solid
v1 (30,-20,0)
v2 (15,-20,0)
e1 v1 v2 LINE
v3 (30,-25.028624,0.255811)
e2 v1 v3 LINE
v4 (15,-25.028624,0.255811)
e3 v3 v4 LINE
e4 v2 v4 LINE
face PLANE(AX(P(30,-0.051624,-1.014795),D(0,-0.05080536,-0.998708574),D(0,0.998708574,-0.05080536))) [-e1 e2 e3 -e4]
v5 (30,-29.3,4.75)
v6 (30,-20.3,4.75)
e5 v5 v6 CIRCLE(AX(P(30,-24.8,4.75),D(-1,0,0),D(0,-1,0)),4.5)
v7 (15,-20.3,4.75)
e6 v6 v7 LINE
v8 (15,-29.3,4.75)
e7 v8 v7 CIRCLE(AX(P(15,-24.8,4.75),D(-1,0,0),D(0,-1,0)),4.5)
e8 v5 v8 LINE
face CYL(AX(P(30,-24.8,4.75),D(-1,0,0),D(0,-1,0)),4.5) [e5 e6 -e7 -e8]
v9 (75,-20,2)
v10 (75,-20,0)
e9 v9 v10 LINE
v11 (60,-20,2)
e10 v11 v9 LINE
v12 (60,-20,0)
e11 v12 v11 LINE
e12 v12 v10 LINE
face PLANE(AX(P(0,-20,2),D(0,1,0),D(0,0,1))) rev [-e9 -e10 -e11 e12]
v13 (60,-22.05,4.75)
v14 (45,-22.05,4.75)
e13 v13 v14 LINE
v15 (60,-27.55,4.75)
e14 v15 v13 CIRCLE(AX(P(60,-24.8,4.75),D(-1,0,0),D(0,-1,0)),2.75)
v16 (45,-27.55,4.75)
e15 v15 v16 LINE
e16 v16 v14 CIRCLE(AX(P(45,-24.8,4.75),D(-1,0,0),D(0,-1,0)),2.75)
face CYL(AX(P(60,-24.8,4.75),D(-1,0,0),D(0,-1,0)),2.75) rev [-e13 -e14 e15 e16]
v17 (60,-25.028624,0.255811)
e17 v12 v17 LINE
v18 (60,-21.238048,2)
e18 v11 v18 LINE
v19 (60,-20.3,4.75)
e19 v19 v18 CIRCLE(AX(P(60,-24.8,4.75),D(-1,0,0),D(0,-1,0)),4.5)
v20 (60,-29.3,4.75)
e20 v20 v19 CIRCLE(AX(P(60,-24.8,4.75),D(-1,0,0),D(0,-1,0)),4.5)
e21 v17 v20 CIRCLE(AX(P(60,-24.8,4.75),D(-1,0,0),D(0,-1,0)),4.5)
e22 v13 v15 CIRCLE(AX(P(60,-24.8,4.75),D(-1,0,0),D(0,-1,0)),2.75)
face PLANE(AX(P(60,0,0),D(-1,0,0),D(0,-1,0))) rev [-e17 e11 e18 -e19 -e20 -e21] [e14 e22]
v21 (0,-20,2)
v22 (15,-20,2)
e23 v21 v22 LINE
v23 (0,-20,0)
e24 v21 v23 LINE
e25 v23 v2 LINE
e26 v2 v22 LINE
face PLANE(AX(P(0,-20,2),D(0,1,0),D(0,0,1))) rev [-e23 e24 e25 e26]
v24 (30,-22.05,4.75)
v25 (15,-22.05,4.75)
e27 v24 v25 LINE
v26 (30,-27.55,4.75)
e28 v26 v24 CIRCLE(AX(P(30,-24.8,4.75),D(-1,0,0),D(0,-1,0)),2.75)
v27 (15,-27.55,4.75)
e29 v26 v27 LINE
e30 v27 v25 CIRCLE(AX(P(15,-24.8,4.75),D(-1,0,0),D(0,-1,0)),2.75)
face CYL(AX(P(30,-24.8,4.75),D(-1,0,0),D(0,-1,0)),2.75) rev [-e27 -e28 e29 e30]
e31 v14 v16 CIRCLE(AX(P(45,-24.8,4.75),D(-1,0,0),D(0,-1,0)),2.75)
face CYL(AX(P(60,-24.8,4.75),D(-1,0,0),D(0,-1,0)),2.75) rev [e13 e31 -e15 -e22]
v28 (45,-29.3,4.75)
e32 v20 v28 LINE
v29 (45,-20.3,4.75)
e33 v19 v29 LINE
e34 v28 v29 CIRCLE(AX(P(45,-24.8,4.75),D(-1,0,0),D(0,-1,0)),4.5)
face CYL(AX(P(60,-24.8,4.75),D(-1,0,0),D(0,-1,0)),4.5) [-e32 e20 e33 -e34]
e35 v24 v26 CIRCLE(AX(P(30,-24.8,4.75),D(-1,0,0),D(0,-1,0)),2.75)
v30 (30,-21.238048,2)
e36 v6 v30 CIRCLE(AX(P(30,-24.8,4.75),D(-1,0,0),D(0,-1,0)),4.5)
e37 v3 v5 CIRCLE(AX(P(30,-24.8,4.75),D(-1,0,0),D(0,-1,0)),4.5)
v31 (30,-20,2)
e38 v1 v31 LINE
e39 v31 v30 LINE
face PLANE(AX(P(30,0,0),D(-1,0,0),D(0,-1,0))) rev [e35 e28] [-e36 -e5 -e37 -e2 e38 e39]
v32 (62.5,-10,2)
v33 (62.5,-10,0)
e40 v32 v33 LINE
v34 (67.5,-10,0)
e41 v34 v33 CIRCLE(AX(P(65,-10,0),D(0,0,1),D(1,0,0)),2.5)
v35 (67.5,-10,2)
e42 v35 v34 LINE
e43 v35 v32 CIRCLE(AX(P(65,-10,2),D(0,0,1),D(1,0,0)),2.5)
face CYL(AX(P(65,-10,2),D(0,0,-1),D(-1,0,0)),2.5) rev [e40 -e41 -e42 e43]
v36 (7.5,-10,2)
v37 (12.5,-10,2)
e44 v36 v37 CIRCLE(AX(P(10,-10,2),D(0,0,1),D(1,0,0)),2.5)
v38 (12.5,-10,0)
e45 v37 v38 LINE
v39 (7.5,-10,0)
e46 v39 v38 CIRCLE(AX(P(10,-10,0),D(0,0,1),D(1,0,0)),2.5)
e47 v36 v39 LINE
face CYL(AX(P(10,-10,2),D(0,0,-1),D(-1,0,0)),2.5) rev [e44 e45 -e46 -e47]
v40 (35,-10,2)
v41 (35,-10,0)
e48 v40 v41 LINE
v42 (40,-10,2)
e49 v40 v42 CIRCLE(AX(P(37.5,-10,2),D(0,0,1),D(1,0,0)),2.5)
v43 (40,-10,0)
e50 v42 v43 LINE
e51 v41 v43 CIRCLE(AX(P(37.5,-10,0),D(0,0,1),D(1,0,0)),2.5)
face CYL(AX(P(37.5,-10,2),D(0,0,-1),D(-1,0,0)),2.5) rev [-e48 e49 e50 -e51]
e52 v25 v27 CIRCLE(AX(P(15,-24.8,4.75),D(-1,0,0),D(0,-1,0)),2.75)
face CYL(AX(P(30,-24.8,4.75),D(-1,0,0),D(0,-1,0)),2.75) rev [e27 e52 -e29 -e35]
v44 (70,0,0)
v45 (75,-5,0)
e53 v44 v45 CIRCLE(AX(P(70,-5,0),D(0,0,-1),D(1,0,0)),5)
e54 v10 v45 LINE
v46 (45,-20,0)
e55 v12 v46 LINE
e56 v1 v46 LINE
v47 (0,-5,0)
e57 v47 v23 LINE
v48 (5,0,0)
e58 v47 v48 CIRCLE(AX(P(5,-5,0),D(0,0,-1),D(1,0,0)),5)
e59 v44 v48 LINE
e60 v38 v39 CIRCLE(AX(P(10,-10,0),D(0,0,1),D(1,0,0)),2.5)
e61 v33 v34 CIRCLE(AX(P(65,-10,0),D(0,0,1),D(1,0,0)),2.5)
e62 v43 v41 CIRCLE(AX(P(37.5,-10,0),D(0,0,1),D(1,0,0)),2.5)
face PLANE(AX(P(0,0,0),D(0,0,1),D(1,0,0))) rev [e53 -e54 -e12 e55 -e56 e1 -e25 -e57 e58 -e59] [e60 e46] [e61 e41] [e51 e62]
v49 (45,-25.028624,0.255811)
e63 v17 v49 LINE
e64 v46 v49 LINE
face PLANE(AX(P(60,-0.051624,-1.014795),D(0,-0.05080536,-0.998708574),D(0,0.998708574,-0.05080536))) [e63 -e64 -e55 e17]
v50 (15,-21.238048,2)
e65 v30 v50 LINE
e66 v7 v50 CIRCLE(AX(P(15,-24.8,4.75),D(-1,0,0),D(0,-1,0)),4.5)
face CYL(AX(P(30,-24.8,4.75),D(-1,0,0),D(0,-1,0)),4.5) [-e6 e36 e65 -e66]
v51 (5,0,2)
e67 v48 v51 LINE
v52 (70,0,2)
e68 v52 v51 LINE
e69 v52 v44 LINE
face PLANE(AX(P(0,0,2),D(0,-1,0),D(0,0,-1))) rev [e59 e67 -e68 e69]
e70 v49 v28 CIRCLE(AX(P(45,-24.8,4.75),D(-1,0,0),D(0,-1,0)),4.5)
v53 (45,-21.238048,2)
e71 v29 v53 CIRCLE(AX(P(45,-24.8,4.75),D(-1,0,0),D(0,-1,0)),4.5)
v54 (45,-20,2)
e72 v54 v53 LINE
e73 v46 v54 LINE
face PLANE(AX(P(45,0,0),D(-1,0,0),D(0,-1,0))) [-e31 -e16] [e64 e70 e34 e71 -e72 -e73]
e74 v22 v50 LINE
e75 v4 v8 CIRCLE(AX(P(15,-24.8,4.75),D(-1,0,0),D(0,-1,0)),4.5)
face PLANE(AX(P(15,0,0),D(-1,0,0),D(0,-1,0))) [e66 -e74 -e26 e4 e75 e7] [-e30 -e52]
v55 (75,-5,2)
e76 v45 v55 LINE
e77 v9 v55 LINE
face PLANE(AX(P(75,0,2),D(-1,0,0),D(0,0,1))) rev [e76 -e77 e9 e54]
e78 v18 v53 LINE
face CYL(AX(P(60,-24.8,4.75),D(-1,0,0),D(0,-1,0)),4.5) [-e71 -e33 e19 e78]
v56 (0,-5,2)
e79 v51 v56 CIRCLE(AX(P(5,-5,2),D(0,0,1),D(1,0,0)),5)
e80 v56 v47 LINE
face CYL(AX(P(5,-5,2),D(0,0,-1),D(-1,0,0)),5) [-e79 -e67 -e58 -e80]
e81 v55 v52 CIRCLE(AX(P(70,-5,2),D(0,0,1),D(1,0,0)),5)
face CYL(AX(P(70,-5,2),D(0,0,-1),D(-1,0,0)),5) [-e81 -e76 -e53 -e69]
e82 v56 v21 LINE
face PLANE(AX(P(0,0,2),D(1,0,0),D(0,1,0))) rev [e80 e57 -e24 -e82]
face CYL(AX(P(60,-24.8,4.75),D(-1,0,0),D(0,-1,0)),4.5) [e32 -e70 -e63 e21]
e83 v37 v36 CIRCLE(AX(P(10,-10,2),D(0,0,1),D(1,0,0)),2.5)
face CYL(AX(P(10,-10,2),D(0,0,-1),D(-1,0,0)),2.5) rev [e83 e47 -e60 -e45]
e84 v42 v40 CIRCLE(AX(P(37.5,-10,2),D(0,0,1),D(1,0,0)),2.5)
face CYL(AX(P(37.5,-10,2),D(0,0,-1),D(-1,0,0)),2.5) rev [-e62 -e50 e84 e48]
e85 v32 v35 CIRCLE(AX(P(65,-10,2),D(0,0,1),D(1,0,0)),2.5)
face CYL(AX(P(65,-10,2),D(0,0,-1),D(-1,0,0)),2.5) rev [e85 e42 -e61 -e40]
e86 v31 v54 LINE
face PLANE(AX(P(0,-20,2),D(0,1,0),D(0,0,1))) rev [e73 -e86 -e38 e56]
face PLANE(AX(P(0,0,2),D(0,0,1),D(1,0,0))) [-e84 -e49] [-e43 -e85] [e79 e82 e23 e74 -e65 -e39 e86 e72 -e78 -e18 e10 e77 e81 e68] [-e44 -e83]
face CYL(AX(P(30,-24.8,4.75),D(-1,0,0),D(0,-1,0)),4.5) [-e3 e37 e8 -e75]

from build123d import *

# Parameters (mm, degrees)
SKETCH1_W           = 75
SKETCH1_H           = 20
SKETCH1_R           = 2.5
BOSS_EXTRUDE1_DEPTH = 2
BOSS_EXTRUDE2_START = -15
BOSS_EXTRUDE2_DEPTH = 15
LPATTERN1_COUNT     = 2
LPATTERN1_PITCH     = 30
FILLET1_R           = 5


with BuildPart() as part:
    # Sketch1 → Boss-Extrude1 (new body)
    with BuildSketch(Plane.XY):
        with Locations((37.5, -10)):
            Rectangle(SKETCH1_W, SKETCH1_H)
        with Locations((10, -10)):
            Circle(SKETCH1_R, mode=Mode.SUBTRACT)
        with Locations((65, -10)):
            Circle(SKETCH1_R, mode=Mode.SUBTRACT)
        with Locations((37.5, -10)):
            Circle(SKETCH1_R, mode=Mode.SUBTRACT)
    extrude(amount=BOSS_EXTRUDE1_DEPTH)

    # Sketch2 → Boss-Extrude2 (add)
    # profile 1 of 2: a face of its own
    with BuildSketch(Plane.ZY.offset(BOSS_EXTRUDE2_START)):
        with BuildLine():
            ThreePointArc((2, -28.361951712), (9.25, -24.8), (2, -21.238048288))
            Line((2, -21.238048288), (2, -24.8))
            Line((2, -24.8), (2, -28.361951712))
        make_face()
        with BuildLine():
            ThreePointArc((7.5, -24.8), (4.75, -27.55), (2, -24.8))
            ThreePointArc((2, -24.8), (4.75, -22.05), (7.5, -24.8))
        make_face(mode=Mode.SUBTRACT)
    # profile 2 of 2: a face of its own
    with BuildSketch(Plane.ZY.offset(BOSS_EXTRUDE2_START)):
        with BuildLine():
            Line((2, -21.238048288), (2, -20))
            Line((2, -20), (0, -20))
            Line((0, -20), (0.255811418, -25.028624118))
            ThreePointArc((0.255811418, -25.028624118), (0.762853744, -26.886304085), (2, -28.361951712))
            Line((2, -28.361951712), (2, -24.8))
            Line((2, -24.8), (2, -21.238048288))
        make_face()
    boss_extrude2 = extrude(amount=-BOSS_EXTRUDE2_DEPTH)

    # LPattern1: Boss-Extrude2 ×2
    with Locations(*[(i * LPATTERN1_PITCH, 0, 0) for i in range(1, LPATTERN1_COUNT)]):
        add(boss_extrude2)

    # Fillet1
    fillet1_edges = [part.edges().sort_by_distance(p)[0] for p in [
        (0, 0, 1),
        (75, 0, 1),
    ]]
    fillet(fillet1_edges, radius=FILLET1_R)


solid = part.part
